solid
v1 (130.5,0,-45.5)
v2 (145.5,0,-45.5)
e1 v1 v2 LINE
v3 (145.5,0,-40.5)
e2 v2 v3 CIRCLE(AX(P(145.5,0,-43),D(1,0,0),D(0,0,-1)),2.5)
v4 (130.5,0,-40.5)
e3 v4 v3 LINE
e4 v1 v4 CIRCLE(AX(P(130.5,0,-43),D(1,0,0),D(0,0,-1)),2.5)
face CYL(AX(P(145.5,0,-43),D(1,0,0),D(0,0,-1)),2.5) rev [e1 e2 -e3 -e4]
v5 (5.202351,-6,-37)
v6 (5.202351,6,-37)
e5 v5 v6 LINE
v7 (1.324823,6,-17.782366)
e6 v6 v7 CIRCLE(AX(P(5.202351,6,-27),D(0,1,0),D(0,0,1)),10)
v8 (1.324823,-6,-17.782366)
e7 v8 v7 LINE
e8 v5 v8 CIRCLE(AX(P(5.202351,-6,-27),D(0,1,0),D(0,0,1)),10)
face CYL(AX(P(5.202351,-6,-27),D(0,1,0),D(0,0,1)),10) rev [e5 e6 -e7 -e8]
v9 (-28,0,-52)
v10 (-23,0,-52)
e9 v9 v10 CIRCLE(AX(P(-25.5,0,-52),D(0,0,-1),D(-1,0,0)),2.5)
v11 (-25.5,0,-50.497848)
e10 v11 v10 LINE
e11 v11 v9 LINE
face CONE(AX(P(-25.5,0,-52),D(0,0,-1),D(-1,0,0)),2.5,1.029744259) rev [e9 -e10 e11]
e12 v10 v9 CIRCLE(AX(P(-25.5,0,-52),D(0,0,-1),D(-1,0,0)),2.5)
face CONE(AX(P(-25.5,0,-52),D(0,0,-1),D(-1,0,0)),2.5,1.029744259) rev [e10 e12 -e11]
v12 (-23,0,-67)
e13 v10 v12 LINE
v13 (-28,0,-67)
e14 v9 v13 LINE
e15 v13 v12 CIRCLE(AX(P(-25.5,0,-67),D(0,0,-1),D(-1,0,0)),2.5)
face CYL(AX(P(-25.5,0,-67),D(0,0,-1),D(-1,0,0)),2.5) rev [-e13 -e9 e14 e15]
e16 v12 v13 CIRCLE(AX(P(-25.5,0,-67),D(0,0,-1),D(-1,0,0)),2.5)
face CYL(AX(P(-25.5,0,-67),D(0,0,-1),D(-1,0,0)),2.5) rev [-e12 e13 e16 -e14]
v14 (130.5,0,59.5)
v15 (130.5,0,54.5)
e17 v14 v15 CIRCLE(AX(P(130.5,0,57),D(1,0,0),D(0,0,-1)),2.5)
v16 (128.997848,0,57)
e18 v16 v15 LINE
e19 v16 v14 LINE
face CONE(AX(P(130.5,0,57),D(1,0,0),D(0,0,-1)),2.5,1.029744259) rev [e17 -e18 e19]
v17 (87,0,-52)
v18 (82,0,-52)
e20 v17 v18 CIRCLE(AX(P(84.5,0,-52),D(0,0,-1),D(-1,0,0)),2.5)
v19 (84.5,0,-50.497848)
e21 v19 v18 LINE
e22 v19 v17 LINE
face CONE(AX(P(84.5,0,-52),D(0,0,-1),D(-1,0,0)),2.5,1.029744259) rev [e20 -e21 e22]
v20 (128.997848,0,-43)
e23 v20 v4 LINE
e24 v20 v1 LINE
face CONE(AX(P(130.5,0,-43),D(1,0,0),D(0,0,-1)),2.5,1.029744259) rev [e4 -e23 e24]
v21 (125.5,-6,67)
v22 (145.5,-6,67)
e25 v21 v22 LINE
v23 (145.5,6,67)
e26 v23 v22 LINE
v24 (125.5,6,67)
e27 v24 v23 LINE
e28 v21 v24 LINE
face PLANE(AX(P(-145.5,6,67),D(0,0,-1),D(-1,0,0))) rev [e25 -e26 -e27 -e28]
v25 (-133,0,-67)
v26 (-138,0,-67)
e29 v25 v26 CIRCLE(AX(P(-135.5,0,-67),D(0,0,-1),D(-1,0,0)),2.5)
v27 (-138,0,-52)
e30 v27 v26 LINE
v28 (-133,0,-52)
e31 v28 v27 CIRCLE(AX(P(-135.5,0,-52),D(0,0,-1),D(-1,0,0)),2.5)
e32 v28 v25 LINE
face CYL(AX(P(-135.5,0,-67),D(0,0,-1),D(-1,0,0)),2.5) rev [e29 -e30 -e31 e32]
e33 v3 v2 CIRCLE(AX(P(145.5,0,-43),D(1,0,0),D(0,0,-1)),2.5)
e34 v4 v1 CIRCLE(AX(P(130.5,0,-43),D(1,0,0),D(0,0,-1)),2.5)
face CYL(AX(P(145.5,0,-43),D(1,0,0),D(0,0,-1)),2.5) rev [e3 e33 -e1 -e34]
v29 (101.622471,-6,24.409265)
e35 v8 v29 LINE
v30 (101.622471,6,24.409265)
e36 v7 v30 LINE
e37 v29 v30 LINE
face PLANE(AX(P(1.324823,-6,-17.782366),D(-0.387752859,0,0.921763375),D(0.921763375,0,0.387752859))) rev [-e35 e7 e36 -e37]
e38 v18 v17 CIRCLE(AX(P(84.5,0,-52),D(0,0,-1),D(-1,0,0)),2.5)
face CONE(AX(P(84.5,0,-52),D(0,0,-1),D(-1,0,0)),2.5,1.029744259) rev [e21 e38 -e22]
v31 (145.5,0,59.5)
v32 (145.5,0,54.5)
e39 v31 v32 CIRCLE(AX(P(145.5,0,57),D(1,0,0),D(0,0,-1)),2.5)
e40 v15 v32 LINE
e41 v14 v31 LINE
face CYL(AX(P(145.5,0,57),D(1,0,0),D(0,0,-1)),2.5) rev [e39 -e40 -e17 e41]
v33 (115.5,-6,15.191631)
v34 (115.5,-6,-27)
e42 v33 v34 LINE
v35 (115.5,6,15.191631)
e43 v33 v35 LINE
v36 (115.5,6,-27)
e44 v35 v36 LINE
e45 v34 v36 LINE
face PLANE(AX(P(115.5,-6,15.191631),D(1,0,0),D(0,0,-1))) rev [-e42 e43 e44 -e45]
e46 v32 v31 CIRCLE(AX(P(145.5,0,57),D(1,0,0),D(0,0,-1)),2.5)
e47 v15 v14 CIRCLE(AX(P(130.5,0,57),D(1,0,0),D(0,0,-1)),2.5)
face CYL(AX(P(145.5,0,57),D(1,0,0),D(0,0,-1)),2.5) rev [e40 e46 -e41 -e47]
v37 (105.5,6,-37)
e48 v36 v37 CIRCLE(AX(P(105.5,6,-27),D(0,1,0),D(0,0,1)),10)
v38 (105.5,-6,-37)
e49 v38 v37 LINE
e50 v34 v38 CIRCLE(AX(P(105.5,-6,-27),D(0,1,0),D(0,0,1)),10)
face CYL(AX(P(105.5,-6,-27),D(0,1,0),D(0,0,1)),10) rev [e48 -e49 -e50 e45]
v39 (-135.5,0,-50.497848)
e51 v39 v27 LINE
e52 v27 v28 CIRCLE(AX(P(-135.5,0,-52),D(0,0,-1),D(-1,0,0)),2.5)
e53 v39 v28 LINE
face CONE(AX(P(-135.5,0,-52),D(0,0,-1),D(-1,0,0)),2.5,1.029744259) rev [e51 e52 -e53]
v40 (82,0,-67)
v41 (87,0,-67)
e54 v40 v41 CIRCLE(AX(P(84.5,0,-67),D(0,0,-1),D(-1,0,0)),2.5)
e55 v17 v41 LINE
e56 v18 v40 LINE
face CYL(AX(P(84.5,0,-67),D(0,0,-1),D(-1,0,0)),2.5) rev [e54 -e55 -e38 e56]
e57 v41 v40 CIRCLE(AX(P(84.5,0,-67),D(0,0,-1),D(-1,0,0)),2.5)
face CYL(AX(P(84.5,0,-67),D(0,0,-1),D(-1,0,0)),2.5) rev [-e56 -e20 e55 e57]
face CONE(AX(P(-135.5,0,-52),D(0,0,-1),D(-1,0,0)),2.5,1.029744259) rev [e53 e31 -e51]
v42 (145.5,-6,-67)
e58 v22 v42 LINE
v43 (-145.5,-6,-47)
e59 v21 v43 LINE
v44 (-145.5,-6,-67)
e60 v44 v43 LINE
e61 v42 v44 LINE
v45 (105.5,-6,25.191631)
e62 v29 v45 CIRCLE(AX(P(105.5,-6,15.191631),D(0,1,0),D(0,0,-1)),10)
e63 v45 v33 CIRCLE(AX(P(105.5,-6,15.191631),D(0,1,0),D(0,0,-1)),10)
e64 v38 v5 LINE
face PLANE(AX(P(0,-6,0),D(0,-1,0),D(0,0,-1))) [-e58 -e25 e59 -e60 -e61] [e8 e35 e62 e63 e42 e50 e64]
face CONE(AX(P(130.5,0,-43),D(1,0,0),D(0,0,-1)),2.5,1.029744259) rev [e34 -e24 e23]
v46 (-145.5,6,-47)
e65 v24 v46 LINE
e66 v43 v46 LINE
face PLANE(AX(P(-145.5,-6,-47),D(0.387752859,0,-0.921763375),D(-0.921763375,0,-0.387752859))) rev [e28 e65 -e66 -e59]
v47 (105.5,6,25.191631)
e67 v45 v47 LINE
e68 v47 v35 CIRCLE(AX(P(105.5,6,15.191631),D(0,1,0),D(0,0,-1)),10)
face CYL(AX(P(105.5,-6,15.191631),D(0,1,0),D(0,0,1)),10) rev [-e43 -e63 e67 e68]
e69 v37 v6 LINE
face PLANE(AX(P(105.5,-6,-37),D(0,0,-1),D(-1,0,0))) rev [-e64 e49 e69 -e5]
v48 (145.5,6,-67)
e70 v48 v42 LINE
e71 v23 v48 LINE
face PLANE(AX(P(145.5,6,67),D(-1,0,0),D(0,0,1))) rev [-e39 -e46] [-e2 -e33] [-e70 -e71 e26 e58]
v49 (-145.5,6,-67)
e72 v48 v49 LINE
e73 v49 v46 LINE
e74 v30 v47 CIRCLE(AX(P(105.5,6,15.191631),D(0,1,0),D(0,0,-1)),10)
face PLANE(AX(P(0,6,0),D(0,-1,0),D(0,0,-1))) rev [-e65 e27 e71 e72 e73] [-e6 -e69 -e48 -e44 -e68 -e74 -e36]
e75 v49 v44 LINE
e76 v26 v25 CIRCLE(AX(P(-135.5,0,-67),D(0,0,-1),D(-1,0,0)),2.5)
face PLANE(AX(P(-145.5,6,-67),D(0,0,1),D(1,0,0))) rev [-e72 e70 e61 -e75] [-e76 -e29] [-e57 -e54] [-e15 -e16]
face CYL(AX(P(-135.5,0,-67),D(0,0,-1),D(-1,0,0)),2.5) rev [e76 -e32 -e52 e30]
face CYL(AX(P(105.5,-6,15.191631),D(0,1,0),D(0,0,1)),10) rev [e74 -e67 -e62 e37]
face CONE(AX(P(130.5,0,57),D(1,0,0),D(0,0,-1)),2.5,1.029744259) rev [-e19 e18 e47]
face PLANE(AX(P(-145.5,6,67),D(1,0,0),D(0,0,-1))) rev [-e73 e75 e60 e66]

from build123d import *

# Parameters (mm, degrees)
SKETCH_1_W             = 291
SKETCH_1_H             = 134
EXTRUDE_1_DEPTH        = 6
CUT_EXTRUDE_1_DEPTH    = 161.633900532
HOLE_WIZARD_M6_1_D     = 5
HOLE_WIZARD_M6_1_DEPTH = 15
HOLE_WIZARD_M6_1_TIP   = 1.502151548
HOLE_WIZARD_M6_2_D     = 5
HOLE_WIZARD_M6_2_DEPTH = 15
HOLE_WIZARD_M6_2_TIP   = 1.502151548


with BuildPart() as part:
    # 草图1 → 凸台-拉伸1 (new, symmetric)
    with BuildSketch(Plane(origin=(0, 0, 0), x_dir=(1, 0, 0), z_dir=(0, 1, 0))):
        Rectangle(SKETCH_1_W, SKETCH_1_H)
    extrude(amount=EXTRUDE_1_DEPTH, both=True)

    # 草图2 → 切除-拉伸1 (cut, through all)
    with BuildSketch(Plane(origin=(0, 6, 0), x_dir=(1, 0, 0), z_dir=(0, 1, 0))):
        Polygon((-145.5, -67), (125.5, -67), (-145.5, 47), align=None)
        with BuildLine():
            Line((115.5, -15.191630897), (115.5, 27))
            ThreePointArc((115.5, 27), (112.571067812, 34.071067812), (105.5, 37))
            Line((105.5, 37), (5.202351114, 37))
            ThreePointArc((5.202351114, 37), (-4.600106168, 28.977834985), (1.324822524, 17.782366246))
            Line((1.324822524, 17.782366246), (101.62247141, -24.409264651))
            ThreePointArc((101.62247141, -24.409264651), (111.032843487, -23.521555443), (115.5, -15.191630897))
        make_face()
    extrude(amount=-CUT_EXTRUDE_1_DEPTH, mode=Mode.SUBTRACT)

    # M6 螺纹孔1
    with Locations(Plane(origin=(145.5, 0, 0), x_dir=(0, 0, -1), z_dir=(1, 0, 0))):
        with Locations((-57, 0), (43, 0)):
            Hole(HOLE_WIZARD_M6_1_D / 2, depth=HOLE_WIZARD_M6_1_DEPTH)
            with Locations((0, 0, -(HOLE_WIZARD_M6_1_DEPTH + HOLE_WIZARD_M6_1_TIP / 2))):  # 118° drill point
                Cone(0, HOLE_WIZARD_M6_1_D / 2, HOLE_WIZARD_M6_1_TIP, mode=Mode.SUBTRACT)

    # M6 螺纹孔2
    with Locations(Plane(origin=(0, 0, -67), x_dir=(-1, 0, 0), z_dir=(0, 0, -1))):
        with Locations((135.5, 0), (25.5, 0), (-84.5, 0)):
            Hole(HOLE_WIZARD_M6_2_D / 2, depth=HOLE_WIZARD_M6_2_DEPTH)
            with Locations((0, 0, -(HOLE_WIZARD_M6_2_DEPTH + HOLE_WIZARD_M6_2_TIP / 2))):  # 118° drill point
                Cone(0, HOLE_WIZARD_M6_2_D / 2, HOLE_WIZARD_M6_2_TIP, mode=Mode.SUBTRACT)


solid = part.part
